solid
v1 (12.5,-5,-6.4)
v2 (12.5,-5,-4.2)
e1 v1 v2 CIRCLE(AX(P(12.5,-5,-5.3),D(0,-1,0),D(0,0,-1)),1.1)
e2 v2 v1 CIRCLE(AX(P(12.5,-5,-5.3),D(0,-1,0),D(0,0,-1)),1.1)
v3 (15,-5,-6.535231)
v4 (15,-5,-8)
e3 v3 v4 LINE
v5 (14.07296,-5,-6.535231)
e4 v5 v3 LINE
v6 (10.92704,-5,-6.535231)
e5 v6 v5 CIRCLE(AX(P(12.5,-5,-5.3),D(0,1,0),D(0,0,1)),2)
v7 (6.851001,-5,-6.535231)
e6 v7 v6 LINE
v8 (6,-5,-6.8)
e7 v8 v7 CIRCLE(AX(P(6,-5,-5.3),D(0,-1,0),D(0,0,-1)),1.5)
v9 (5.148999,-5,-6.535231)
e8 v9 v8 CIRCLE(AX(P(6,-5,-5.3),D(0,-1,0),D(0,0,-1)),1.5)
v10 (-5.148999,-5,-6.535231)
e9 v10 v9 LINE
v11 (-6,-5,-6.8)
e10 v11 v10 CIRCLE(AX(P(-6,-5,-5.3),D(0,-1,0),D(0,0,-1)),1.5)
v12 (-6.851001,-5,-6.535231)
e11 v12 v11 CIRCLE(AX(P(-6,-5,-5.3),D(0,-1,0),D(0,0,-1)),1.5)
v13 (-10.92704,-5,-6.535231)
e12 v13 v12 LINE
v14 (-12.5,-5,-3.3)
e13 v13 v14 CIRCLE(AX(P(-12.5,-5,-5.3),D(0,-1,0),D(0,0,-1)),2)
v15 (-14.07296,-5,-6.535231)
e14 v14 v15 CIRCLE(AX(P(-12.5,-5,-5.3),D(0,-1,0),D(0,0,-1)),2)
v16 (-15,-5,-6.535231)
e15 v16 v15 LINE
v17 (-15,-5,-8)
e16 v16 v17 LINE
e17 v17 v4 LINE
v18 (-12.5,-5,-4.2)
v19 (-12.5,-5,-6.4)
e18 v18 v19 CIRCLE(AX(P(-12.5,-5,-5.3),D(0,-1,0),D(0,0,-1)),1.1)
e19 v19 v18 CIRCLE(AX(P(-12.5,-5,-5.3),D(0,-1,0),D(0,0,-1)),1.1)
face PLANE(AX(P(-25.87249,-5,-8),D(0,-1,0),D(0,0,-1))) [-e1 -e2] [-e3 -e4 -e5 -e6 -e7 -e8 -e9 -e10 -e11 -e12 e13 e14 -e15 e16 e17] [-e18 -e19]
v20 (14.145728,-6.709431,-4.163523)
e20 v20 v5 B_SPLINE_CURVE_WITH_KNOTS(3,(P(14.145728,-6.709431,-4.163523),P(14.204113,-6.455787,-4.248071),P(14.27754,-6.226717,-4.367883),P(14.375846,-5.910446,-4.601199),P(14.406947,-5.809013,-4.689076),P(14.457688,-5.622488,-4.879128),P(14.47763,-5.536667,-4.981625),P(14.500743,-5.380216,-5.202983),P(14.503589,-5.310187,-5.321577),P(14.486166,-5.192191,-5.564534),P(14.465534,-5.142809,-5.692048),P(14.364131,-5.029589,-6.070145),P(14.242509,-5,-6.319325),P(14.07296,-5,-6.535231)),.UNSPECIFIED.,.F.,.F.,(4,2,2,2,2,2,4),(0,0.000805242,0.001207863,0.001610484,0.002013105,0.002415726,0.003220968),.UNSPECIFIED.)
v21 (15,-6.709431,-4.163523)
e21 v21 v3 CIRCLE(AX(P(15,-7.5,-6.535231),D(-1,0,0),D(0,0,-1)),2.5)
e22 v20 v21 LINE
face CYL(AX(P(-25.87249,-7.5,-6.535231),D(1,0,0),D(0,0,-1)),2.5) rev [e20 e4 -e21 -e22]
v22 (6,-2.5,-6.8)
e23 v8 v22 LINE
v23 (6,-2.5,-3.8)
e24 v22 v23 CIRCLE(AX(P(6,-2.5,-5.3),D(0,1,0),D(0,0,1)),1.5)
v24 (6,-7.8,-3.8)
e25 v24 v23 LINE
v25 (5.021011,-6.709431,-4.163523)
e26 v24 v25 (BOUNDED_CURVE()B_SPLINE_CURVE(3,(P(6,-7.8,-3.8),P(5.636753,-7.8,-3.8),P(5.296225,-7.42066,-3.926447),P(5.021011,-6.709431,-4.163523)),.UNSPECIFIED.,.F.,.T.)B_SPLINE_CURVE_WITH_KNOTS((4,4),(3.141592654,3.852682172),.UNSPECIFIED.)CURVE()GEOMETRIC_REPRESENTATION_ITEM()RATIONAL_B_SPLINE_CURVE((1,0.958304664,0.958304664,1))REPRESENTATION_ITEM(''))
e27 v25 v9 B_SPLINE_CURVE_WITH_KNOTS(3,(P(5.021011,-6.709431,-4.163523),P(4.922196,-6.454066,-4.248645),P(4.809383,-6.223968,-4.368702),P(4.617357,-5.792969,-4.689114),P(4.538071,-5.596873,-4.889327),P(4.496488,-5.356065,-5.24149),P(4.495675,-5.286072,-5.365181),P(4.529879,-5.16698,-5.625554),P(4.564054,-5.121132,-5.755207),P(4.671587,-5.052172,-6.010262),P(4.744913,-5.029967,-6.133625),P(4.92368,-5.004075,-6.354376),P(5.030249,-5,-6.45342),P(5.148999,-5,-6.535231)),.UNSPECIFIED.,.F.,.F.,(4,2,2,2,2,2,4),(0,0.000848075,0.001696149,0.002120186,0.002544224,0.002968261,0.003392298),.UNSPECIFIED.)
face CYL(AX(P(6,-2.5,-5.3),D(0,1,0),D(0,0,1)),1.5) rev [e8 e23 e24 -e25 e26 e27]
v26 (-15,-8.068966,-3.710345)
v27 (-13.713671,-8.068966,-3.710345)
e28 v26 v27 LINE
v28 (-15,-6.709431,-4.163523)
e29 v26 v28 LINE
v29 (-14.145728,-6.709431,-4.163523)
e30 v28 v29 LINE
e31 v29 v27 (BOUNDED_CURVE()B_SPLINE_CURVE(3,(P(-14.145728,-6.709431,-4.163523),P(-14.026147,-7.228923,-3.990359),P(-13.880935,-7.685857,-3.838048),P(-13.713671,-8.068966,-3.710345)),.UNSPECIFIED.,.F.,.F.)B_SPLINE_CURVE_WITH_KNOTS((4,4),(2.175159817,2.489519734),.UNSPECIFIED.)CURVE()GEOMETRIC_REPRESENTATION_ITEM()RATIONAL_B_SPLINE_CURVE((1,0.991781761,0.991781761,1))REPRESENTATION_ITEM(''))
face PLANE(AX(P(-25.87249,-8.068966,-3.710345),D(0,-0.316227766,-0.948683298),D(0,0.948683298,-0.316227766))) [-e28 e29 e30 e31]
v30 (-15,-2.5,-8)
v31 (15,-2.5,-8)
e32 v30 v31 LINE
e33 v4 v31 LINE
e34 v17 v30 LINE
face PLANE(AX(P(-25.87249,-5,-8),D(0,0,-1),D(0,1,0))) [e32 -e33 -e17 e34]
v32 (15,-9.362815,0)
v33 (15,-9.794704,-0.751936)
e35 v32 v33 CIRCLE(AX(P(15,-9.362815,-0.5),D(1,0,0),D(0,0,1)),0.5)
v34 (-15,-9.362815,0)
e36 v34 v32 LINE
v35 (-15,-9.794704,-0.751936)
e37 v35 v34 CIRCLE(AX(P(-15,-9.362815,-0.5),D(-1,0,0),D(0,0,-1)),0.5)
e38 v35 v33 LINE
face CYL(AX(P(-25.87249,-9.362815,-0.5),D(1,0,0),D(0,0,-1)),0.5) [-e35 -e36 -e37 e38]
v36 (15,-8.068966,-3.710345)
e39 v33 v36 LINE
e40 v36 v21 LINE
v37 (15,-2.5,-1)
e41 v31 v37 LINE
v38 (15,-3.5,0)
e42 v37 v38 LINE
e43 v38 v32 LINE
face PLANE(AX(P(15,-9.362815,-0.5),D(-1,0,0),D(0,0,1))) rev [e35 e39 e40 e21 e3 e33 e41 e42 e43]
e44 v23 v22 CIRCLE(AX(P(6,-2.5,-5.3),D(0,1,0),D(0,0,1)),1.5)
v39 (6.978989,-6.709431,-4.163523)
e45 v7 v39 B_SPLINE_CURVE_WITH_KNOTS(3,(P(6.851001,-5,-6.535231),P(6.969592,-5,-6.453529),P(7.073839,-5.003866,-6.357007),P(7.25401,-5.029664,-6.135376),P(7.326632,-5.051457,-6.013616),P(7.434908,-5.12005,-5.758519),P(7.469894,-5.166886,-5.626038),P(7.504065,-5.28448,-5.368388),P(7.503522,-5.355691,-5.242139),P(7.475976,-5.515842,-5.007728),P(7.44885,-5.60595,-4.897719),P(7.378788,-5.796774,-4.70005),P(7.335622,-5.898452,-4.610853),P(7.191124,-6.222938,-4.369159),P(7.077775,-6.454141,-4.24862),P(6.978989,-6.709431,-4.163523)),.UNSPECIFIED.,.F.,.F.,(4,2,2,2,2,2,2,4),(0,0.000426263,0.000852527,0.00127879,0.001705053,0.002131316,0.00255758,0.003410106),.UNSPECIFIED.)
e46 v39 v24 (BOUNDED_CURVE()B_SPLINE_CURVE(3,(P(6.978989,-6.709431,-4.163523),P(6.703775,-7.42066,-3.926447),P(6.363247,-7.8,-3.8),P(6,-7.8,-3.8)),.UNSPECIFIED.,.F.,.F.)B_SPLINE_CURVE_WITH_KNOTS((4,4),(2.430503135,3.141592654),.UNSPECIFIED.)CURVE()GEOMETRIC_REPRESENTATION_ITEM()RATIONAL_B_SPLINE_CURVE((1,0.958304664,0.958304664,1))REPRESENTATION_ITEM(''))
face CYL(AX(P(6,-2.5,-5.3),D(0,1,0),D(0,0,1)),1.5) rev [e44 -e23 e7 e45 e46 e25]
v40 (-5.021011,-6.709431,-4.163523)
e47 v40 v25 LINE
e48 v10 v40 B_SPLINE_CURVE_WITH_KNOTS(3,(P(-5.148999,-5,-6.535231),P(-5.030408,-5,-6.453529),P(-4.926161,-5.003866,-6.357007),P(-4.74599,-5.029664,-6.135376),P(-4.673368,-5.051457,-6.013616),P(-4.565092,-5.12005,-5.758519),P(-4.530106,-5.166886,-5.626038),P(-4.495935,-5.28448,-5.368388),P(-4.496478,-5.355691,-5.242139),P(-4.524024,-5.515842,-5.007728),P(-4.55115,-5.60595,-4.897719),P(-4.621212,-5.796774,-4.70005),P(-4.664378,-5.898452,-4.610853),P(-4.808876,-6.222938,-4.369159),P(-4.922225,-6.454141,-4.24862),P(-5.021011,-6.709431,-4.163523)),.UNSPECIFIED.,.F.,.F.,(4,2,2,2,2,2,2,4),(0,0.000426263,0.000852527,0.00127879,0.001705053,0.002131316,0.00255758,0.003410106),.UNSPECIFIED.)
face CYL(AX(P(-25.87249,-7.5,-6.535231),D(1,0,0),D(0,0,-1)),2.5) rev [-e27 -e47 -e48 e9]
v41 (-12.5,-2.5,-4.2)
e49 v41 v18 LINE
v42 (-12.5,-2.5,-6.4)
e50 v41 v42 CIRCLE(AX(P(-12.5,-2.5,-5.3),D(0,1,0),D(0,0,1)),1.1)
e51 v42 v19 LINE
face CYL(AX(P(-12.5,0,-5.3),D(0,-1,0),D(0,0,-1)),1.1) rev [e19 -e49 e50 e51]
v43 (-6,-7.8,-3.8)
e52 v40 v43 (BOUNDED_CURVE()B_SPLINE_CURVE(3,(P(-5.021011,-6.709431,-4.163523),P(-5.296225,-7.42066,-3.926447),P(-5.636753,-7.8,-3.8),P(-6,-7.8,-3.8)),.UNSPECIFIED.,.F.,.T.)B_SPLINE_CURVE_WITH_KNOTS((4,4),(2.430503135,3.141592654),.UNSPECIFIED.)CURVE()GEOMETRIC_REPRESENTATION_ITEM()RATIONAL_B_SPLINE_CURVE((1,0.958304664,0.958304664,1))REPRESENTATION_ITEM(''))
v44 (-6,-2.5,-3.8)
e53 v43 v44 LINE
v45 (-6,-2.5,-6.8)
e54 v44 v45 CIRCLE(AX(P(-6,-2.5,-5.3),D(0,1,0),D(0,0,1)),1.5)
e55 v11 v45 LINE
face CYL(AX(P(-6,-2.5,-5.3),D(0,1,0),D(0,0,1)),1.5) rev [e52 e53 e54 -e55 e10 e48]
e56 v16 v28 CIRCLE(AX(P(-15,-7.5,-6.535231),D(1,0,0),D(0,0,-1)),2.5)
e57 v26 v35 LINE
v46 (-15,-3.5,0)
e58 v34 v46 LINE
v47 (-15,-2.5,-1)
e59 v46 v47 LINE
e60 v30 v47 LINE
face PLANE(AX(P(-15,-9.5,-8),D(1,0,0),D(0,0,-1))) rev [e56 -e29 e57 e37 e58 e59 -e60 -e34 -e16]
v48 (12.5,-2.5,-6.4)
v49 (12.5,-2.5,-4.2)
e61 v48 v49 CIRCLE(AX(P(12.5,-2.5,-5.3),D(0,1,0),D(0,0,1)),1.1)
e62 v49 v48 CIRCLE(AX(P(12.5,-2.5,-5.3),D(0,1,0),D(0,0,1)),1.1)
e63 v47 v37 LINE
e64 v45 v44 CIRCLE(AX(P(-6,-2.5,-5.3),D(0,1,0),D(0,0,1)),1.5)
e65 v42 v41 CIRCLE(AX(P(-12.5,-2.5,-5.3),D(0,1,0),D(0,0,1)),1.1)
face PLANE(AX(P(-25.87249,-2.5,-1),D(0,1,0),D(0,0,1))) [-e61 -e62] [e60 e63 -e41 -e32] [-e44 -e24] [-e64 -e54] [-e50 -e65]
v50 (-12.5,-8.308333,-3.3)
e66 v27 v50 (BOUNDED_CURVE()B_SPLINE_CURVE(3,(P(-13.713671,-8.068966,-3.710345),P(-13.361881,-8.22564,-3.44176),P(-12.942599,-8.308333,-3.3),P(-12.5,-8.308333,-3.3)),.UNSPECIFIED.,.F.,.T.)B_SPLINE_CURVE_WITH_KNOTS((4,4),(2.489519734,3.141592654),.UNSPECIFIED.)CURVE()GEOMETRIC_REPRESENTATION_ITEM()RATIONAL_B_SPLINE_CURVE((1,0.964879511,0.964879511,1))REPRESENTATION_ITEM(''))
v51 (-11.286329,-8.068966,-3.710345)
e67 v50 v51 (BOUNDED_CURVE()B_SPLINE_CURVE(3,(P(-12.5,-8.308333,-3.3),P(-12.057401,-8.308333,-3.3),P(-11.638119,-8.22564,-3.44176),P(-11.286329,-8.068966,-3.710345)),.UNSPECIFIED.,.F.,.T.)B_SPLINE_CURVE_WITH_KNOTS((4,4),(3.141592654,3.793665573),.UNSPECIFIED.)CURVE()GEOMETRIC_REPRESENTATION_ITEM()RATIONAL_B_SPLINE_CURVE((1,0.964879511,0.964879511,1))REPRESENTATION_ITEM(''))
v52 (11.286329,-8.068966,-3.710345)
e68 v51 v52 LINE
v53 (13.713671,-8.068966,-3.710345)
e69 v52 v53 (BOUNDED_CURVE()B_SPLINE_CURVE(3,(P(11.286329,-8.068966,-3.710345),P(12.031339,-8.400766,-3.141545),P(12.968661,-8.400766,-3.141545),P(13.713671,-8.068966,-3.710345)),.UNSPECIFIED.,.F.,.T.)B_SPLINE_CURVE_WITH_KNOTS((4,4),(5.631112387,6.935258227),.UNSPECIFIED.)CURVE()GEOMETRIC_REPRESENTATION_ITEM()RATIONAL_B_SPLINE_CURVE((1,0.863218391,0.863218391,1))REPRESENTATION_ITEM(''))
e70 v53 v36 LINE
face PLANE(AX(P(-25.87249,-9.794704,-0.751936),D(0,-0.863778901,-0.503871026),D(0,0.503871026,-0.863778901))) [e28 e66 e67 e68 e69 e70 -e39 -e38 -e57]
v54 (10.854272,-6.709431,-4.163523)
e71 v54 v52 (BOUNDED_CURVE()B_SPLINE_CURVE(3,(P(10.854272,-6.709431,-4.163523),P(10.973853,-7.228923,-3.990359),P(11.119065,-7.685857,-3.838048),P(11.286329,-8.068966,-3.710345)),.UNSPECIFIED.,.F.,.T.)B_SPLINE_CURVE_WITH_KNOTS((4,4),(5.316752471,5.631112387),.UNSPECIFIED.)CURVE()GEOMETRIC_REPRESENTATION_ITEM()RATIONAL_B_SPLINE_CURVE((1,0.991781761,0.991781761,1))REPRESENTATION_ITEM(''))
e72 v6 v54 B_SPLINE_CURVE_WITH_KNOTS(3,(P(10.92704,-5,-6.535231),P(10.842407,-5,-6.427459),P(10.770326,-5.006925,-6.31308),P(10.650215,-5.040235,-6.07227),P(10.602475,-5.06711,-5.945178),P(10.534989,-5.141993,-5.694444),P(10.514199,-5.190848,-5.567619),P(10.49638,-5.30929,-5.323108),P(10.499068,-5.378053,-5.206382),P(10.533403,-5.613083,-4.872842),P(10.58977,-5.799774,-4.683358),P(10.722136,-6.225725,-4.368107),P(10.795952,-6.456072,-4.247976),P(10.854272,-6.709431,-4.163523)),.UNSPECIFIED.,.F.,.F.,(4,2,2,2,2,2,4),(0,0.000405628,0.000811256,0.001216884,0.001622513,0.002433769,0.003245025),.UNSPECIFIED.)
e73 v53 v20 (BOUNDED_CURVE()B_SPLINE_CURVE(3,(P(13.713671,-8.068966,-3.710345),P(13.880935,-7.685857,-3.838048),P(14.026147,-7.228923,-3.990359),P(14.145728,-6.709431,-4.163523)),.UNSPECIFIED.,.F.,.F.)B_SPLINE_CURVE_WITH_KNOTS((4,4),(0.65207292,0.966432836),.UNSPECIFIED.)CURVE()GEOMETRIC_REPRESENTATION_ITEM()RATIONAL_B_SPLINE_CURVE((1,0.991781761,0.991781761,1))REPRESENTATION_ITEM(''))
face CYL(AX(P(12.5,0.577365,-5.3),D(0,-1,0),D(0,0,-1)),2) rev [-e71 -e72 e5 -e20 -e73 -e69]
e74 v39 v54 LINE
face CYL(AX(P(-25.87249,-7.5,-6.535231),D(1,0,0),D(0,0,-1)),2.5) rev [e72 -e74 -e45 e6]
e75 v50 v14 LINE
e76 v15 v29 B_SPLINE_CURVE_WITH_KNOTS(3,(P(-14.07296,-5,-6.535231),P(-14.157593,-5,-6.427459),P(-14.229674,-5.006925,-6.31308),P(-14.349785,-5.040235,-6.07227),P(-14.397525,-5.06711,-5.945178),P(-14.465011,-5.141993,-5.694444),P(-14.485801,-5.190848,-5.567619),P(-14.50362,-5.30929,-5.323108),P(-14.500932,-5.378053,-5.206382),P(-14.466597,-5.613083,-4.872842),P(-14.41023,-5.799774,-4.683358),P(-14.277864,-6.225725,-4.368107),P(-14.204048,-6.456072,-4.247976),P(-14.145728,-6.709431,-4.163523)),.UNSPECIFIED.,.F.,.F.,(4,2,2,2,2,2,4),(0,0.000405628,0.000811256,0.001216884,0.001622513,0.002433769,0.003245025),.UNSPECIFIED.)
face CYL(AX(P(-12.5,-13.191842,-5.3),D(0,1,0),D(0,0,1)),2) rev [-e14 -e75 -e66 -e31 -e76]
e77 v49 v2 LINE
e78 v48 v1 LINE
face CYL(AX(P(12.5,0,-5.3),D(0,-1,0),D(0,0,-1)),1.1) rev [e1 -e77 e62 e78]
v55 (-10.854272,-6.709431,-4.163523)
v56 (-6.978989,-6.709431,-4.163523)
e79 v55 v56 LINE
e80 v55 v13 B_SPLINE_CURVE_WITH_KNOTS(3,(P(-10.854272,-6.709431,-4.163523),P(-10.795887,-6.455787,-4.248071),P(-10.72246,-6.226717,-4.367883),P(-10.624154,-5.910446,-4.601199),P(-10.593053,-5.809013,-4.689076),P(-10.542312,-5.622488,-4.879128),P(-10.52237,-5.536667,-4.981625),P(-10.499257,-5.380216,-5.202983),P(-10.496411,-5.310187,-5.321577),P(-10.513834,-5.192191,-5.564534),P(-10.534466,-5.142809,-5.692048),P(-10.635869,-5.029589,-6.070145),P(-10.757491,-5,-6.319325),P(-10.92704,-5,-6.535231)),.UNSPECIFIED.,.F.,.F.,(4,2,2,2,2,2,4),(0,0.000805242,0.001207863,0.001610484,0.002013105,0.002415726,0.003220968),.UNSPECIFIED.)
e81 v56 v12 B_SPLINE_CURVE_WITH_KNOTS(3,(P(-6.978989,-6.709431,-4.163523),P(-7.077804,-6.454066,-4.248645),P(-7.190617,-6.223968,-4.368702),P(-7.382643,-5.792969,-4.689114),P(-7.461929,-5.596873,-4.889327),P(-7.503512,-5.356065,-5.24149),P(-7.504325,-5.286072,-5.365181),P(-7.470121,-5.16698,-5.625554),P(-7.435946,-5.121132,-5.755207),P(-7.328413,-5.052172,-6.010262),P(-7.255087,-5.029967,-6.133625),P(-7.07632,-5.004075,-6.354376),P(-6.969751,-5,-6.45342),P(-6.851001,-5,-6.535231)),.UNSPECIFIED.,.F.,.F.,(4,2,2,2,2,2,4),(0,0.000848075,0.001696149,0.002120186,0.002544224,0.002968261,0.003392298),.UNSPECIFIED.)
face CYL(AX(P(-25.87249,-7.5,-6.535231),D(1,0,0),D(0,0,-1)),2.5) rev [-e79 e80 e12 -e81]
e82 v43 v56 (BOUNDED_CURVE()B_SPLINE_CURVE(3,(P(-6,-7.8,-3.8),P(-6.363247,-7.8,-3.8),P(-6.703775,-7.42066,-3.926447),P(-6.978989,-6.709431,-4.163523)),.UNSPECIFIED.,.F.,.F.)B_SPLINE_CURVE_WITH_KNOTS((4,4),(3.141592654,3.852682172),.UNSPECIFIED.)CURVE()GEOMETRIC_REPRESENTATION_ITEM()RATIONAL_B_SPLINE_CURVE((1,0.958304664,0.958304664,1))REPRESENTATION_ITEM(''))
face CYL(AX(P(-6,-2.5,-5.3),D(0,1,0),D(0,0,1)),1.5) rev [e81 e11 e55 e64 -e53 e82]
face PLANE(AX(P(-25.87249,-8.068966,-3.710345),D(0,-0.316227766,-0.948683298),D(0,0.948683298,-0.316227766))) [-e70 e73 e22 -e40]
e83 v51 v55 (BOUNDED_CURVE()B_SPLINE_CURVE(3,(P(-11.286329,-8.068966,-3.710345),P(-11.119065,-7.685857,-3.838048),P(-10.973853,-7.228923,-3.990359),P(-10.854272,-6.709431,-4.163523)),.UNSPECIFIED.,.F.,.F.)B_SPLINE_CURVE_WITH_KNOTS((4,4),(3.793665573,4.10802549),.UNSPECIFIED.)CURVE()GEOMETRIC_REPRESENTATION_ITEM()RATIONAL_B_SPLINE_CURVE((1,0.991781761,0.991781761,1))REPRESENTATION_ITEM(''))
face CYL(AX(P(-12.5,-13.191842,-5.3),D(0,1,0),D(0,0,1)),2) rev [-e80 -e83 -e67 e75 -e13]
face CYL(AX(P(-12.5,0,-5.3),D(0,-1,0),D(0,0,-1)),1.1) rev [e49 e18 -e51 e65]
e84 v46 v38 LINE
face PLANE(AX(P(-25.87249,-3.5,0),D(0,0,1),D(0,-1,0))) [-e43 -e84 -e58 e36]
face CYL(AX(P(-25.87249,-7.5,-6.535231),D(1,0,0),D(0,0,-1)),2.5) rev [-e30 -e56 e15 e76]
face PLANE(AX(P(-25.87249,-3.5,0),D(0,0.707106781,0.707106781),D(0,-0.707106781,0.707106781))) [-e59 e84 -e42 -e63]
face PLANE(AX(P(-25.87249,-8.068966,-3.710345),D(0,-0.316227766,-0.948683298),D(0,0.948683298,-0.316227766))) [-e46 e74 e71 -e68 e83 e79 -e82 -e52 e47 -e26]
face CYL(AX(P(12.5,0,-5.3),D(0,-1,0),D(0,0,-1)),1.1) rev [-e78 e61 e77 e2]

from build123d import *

# Parameters (mm, degrees)
EXTRUDE_1_DEPTH     = 30
MM_1_D              = 3
CUT_EXTRUDE_1_DEPTH = 3.5
CUT_EXTRUDE_2_REACH = 19.682
SKETCH_15_R         = 1.1
CUT_EXTRUDE_3_DEPTH = 5


with BuildPart() as part:
    # 草图2 → 凸台-拉伸1 (new body)
    with BuildSketch(Plane(origin=(15, 0, 0), x_dir=(0, 0, -1), z_dir=(1, 0, 0))):
        with BuildLine():
            Line((0, -3.5), (1, -2.5))
            Line((1, -2.5), (8, -2.5))
            Line((8, -2.5), (8, -5))
            Line((8, -5), (6.535231383, -5))
            ThreePointArc((6.535231383, -5), (5.073455672, -5.471894537), (4.163523138, -6.709430585))
            Line((4.163523138, -6.709430585), (3.710344828, -8.068965517))
            Line((3.710344828, -8.068965517), (0.751935513, -9.794704284))
            ThreePointArc((0.751935513, -9.794704284), (0.250969637, -9.79638591), (0, -9.362814834))
            Line((0, -9.362814834), (0, -3.5))
        make_face()
    extrude(amount=-EXTRUDE_1_DEPTH)

    # 大小mm 暗销孔1 (through all)
    with Locations(Plane(origin=(0, -2.5, 0), x_dir=(1, 0, 0), z_dir=(0, 1, 0))):
        with Locations((6, 5.3), (-6, 5.3)):
            Hole(MM_1_D / 2)

    # 草图13 → 切除-拉伸1 (cut)
    with BuildSketch(Plane(origin=(0, -8.5, 0), x_dir=(1, 0, 0), z_dir=(0, 1, 0))):
        with BuildLine():
            ThreePointArc((10.927039915, 6.535231383), (12.5, 3.3), (14.072960085, 6.535231383))
            ThreePointArc((14.072960085, 6.535231383), (12.5, 7.186772784), (10.927039915, 6.535231383))
        make_face()
    extrude(amount=CUT_EXTRUDE_1_DEPTH, mode=Mode.SUBTRACT)

    # 草图14 → 切除-拉伸2 (cut, up to next)
    with BuildSketch(Plane.XZ.offset(5), mode=Mode.PRIVATE) as cut_extrude_2_sk1:
        with BuildLine():
            ThreePointArc((-10.927039915, -6.535231383), (-12.5, -3.3), (-14.072960085, -6.535231383))
            ThreePointArc((-14.072960085, -6.535231383), (-12.5, -7.186772784), (-10.927039915, -6.535231383))
        make_face()
    cut_extrude_2_tool1 = extrude(cut_extrude_2_sk1.sketch, amount=CUT_EXTRUDE_2_REACH, mode=Mode.PRIVATE) & part.part
    add(cut_extrude_2_tool1.solids().sort_by_distance((-12.5, -5, -5.261226))[0], mode=Mode.SUBTRACT)

    # 草图15 → 切除-拉伸3 (cut)
    with BuildSketch(Plane.XZ.offset(5)):
        with Locations(Location((12.5, -5.3, 0), (0, 0, 270))):
            Circle(SKETCH_15_R)
        with Locations(Location((-12.5, -5.3, 0), (0, 0, 270))):
            Circle(SKETCH_15_R)
    extrude(amount=-CUT_EXTRUDE_3_DEPTH, mode=Mode.SUBTRACT)


solid = part.part
